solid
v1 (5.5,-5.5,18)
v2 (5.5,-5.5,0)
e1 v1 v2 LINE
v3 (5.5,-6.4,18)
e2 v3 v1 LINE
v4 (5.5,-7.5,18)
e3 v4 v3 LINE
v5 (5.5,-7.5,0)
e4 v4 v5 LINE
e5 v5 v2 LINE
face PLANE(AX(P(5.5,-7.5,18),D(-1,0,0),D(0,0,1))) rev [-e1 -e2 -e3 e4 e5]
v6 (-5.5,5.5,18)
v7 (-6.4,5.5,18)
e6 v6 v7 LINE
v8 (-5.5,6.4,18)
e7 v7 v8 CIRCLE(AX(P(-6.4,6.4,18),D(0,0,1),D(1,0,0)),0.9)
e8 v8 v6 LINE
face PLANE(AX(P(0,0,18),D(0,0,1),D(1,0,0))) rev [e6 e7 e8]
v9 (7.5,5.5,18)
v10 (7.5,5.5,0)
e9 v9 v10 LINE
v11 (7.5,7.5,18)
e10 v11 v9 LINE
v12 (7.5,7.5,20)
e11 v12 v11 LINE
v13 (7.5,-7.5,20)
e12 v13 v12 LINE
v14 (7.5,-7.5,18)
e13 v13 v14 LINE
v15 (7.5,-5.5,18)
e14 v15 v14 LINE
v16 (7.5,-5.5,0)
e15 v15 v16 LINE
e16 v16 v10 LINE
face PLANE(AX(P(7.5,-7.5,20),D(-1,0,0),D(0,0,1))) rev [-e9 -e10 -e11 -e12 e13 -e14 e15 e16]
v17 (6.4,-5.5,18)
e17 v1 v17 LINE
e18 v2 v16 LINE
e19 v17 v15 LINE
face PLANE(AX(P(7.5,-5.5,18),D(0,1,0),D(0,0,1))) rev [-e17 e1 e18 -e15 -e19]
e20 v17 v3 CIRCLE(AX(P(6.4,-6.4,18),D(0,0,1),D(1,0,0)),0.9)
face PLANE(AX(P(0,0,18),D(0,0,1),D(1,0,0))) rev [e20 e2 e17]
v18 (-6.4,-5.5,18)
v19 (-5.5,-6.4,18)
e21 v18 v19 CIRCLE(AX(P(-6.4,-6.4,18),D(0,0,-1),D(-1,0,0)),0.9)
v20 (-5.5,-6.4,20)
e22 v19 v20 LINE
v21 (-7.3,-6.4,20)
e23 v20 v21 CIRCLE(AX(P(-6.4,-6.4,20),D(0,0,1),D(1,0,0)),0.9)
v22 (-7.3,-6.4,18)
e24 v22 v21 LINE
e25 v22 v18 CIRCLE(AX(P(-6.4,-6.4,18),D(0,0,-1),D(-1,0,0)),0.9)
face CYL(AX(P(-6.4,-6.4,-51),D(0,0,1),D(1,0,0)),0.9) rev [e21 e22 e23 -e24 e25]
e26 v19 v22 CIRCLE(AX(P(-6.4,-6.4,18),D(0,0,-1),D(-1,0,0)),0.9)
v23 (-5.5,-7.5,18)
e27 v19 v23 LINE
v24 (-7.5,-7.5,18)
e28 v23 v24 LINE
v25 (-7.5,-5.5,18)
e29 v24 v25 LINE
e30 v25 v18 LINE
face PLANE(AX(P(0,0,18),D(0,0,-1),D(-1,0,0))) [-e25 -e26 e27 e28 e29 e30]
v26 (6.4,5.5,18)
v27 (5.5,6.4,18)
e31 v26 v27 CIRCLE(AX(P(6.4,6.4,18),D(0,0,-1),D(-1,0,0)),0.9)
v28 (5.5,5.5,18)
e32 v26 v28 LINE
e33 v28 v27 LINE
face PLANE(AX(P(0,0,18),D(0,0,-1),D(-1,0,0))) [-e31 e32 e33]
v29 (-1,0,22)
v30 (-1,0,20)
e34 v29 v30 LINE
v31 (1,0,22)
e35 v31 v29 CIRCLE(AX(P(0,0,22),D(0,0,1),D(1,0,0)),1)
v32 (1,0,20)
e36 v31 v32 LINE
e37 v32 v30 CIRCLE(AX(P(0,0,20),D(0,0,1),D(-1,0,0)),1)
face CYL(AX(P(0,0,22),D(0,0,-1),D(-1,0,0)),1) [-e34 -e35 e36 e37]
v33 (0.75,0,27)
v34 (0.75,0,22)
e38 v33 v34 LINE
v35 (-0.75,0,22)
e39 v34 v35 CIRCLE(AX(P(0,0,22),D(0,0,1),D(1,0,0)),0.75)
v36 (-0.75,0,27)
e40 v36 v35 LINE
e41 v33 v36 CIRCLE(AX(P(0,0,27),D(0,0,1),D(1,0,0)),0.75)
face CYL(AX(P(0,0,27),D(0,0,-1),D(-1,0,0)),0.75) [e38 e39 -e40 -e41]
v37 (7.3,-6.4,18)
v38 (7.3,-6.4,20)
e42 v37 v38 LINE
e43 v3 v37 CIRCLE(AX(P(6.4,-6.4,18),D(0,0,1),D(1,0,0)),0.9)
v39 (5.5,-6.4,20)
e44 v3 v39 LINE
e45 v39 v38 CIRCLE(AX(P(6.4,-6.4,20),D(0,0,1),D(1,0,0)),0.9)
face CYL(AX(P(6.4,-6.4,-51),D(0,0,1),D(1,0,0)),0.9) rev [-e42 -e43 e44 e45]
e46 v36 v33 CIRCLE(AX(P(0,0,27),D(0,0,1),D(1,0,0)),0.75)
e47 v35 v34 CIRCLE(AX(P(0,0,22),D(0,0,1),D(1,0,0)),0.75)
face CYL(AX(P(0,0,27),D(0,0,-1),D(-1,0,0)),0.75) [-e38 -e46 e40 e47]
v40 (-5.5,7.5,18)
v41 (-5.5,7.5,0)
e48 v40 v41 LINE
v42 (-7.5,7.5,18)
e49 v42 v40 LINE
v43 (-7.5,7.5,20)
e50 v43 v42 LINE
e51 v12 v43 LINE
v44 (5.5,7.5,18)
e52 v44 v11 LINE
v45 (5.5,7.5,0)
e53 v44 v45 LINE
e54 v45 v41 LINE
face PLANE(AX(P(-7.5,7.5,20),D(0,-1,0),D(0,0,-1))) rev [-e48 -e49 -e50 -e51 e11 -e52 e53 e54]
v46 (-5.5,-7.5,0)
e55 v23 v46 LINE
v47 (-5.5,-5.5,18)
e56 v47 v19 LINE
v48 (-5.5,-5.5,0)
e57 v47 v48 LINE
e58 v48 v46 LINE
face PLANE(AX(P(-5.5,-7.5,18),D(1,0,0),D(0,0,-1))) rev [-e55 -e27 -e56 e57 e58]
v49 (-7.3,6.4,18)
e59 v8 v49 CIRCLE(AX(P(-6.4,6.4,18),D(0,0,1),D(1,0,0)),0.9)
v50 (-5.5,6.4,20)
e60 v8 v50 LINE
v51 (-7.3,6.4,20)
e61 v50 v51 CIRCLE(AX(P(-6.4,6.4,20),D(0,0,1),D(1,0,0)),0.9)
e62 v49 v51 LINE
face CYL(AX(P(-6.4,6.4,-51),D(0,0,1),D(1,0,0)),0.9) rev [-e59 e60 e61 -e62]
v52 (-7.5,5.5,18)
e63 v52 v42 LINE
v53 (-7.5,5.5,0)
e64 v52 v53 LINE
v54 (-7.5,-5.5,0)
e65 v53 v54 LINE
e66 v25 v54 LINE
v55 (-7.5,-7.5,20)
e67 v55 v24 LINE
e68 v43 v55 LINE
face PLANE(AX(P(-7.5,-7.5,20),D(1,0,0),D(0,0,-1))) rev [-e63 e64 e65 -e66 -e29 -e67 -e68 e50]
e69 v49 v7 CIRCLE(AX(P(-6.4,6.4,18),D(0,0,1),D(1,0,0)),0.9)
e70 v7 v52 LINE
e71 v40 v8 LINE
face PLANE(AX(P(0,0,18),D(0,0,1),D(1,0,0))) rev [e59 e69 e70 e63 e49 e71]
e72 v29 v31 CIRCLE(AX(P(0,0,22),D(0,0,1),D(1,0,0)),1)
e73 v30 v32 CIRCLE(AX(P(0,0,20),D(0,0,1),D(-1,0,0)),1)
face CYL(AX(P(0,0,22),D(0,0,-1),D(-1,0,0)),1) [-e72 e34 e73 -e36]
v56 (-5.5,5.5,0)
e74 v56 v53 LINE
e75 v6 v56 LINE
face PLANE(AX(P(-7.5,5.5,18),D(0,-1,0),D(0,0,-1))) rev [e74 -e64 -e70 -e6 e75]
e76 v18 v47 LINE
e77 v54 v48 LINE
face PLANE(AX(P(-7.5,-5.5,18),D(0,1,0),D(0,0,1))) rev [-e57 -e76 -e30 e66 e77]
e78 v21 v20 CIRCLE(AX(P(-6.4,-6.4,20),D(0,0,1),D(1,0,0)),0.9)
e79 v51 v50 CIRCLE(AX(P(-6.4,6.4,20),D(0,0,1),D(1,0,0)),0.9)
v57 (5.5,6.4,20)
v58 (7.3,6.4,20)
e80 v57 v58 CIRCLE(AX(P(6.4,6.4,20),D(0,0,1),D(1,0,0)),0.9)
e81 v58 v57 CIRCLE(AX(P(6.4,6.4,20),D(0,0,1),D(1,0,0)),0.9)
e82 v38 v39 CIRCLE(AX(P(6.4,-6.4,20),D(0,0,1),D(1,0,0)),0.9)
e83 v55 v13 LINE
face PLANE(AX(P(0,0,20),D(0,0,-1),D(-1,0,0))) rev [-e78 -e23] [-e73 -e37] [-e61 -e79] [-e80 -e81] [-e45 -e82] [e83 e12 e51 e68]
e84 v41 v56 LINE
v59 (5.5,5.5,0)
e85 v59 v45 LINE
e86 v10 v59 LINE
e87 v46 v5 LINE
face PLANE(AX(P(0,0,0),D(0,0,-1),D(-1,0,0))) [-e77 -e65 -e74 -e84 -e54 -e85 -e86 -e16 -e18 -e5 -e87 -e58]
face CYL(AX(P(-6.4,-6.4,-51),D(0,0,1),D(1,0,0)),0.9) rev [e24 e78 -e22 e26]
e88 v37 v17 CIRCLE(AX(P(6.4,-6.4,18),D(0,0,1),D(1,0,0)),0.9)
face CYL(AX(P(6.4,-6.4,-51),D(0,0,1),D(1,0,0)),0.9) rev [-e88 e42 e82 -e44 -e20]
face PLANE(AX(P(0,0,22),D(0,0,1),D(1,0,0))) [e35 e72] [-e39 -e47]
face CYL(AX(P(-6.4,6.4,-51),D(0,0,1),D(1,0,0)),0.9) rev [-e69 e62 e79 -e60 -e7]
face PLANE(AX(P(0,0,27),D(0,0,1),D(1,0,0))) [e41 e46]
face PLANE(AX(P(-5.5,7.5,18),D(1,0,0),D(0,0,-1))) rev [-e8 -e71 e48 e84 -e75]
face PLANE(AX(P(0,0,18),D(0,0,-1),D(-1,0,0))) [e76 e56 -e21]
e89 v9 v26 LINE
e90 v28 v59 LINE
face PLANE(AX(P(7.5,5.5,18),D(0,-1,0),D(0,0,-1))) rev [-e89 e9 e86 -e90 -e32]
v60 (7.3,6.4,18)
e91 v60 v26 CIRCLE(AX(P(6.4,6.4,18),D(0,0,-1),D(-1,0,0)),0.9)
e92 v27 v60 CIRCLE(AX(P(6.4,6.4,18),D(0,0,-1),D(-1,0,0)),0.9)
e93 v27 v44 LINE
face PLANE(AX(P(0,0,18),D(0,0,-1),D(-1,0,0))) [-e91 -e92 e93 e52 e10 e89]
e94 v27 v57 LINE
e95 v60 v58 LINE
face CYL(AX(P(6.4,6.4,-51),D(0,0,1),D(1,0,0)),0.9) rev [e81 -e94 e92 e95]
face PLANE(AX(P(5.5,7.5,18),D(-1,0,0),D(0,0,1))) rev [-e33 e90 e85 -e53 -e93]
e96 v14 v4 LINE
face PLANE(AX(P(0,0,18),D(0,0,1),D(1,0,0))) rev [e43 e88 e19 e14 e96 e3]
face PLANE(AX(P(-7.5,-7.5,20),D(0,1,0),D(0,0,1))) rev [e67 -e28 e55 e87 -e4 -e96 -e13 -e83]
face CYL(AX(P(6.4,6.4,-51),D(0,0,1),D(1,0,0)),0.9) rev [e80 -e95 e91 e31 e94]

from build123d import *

# Parameters (mm, degrees)
SKETCH1_W           = 15
SKETCH1_H           = 15
BOSS_EXTRUDE1_DEPTH = 20
SKETCH5_W           = 2
SKETCH5_H           = 2
CUT_EXTRUDE1_DEPTH  = 18
SKETCH2_R           = 0.9
CUT_EXTRUDE2_DEPTH  = 71
SKETCH6_R           = 1
BOSS_EXTRUDE2_DEPTH = 2
SKETCH7_R           = 0.75
BOSS_EXTRUDE3_DEPTH = 5


with BuildPart() as part:
    # Sketch1 → Boss-Extrude1 (new body)
    with BuildSketch(Plane.XY):
        Rectangle(SKETCH1_W, SKETCH1_H)
    extrude(amount=BOSS_EXTRUDE1_DEPTH)

    # Sketch5 → Cut-Extrude1 (cut)
    with BuildSketch(Plane(origin=(0, 0, 0), x_dir=(-1, 0, 0), z_dir=(0, 0, -1))):
        with Locations((6.5, 6.5)):
            Rectangle(SKETCH5_W, SKETCH5_H)
        with Locations((6.5, -6.5)):
            Rectangle(SKETCH5_W, SKETCH5_H)
        with Locations((-6.5, -6.5)):
            Rectangle(SKETCH5_W, SKETCH5_H)
        with Locations((-6.5, 6.5)):
            Rectangle(SKETCH5_W, SKETCH5_H)
    extrude(amount=-CUT_EXTRUDE1_DEPTH, mode=Mode.SUBTRACT)

    # Sketch2 → Cut-Extrude2 (cut)
    with BuildSketch(Plane.XY.offset(20)):
        with Locations((6.4, 6.4)):
            Circle(SKETCH2_R)
        with Locations((-6.4, 6.4)):
            Circle(SKETCH2_R)
        with Locations((-6.4, -6.4)):
            Circle(SKETCH2_R)
        with Locations((6.4, -6.4)):
            Circle(SKETCH2_R)
    extrude(amount=-CUT_EXTRUDE2_DEPTH, mode=Mode.SUBTRACT)

    # Sketch6 → Boss-Extrude2 (add)
    with BuildSketch(Plane.XY.offset(20)):
        with Locations(Location((0, 0, 0), (0, 0, 180))):
            Circle(SKETCH6_R)
    extrude(amount=BOSS_EXTRUDE2_DEPTH)

    # Sketch7 → Boss-Extrude3 (add)
    with BuildSketch(Plane.XY.offset(22)):
        Circle(SKETCH7_R)
    extrude(amount=BOSS_EXTRUDE3_DEPTH)


solid = part.part
